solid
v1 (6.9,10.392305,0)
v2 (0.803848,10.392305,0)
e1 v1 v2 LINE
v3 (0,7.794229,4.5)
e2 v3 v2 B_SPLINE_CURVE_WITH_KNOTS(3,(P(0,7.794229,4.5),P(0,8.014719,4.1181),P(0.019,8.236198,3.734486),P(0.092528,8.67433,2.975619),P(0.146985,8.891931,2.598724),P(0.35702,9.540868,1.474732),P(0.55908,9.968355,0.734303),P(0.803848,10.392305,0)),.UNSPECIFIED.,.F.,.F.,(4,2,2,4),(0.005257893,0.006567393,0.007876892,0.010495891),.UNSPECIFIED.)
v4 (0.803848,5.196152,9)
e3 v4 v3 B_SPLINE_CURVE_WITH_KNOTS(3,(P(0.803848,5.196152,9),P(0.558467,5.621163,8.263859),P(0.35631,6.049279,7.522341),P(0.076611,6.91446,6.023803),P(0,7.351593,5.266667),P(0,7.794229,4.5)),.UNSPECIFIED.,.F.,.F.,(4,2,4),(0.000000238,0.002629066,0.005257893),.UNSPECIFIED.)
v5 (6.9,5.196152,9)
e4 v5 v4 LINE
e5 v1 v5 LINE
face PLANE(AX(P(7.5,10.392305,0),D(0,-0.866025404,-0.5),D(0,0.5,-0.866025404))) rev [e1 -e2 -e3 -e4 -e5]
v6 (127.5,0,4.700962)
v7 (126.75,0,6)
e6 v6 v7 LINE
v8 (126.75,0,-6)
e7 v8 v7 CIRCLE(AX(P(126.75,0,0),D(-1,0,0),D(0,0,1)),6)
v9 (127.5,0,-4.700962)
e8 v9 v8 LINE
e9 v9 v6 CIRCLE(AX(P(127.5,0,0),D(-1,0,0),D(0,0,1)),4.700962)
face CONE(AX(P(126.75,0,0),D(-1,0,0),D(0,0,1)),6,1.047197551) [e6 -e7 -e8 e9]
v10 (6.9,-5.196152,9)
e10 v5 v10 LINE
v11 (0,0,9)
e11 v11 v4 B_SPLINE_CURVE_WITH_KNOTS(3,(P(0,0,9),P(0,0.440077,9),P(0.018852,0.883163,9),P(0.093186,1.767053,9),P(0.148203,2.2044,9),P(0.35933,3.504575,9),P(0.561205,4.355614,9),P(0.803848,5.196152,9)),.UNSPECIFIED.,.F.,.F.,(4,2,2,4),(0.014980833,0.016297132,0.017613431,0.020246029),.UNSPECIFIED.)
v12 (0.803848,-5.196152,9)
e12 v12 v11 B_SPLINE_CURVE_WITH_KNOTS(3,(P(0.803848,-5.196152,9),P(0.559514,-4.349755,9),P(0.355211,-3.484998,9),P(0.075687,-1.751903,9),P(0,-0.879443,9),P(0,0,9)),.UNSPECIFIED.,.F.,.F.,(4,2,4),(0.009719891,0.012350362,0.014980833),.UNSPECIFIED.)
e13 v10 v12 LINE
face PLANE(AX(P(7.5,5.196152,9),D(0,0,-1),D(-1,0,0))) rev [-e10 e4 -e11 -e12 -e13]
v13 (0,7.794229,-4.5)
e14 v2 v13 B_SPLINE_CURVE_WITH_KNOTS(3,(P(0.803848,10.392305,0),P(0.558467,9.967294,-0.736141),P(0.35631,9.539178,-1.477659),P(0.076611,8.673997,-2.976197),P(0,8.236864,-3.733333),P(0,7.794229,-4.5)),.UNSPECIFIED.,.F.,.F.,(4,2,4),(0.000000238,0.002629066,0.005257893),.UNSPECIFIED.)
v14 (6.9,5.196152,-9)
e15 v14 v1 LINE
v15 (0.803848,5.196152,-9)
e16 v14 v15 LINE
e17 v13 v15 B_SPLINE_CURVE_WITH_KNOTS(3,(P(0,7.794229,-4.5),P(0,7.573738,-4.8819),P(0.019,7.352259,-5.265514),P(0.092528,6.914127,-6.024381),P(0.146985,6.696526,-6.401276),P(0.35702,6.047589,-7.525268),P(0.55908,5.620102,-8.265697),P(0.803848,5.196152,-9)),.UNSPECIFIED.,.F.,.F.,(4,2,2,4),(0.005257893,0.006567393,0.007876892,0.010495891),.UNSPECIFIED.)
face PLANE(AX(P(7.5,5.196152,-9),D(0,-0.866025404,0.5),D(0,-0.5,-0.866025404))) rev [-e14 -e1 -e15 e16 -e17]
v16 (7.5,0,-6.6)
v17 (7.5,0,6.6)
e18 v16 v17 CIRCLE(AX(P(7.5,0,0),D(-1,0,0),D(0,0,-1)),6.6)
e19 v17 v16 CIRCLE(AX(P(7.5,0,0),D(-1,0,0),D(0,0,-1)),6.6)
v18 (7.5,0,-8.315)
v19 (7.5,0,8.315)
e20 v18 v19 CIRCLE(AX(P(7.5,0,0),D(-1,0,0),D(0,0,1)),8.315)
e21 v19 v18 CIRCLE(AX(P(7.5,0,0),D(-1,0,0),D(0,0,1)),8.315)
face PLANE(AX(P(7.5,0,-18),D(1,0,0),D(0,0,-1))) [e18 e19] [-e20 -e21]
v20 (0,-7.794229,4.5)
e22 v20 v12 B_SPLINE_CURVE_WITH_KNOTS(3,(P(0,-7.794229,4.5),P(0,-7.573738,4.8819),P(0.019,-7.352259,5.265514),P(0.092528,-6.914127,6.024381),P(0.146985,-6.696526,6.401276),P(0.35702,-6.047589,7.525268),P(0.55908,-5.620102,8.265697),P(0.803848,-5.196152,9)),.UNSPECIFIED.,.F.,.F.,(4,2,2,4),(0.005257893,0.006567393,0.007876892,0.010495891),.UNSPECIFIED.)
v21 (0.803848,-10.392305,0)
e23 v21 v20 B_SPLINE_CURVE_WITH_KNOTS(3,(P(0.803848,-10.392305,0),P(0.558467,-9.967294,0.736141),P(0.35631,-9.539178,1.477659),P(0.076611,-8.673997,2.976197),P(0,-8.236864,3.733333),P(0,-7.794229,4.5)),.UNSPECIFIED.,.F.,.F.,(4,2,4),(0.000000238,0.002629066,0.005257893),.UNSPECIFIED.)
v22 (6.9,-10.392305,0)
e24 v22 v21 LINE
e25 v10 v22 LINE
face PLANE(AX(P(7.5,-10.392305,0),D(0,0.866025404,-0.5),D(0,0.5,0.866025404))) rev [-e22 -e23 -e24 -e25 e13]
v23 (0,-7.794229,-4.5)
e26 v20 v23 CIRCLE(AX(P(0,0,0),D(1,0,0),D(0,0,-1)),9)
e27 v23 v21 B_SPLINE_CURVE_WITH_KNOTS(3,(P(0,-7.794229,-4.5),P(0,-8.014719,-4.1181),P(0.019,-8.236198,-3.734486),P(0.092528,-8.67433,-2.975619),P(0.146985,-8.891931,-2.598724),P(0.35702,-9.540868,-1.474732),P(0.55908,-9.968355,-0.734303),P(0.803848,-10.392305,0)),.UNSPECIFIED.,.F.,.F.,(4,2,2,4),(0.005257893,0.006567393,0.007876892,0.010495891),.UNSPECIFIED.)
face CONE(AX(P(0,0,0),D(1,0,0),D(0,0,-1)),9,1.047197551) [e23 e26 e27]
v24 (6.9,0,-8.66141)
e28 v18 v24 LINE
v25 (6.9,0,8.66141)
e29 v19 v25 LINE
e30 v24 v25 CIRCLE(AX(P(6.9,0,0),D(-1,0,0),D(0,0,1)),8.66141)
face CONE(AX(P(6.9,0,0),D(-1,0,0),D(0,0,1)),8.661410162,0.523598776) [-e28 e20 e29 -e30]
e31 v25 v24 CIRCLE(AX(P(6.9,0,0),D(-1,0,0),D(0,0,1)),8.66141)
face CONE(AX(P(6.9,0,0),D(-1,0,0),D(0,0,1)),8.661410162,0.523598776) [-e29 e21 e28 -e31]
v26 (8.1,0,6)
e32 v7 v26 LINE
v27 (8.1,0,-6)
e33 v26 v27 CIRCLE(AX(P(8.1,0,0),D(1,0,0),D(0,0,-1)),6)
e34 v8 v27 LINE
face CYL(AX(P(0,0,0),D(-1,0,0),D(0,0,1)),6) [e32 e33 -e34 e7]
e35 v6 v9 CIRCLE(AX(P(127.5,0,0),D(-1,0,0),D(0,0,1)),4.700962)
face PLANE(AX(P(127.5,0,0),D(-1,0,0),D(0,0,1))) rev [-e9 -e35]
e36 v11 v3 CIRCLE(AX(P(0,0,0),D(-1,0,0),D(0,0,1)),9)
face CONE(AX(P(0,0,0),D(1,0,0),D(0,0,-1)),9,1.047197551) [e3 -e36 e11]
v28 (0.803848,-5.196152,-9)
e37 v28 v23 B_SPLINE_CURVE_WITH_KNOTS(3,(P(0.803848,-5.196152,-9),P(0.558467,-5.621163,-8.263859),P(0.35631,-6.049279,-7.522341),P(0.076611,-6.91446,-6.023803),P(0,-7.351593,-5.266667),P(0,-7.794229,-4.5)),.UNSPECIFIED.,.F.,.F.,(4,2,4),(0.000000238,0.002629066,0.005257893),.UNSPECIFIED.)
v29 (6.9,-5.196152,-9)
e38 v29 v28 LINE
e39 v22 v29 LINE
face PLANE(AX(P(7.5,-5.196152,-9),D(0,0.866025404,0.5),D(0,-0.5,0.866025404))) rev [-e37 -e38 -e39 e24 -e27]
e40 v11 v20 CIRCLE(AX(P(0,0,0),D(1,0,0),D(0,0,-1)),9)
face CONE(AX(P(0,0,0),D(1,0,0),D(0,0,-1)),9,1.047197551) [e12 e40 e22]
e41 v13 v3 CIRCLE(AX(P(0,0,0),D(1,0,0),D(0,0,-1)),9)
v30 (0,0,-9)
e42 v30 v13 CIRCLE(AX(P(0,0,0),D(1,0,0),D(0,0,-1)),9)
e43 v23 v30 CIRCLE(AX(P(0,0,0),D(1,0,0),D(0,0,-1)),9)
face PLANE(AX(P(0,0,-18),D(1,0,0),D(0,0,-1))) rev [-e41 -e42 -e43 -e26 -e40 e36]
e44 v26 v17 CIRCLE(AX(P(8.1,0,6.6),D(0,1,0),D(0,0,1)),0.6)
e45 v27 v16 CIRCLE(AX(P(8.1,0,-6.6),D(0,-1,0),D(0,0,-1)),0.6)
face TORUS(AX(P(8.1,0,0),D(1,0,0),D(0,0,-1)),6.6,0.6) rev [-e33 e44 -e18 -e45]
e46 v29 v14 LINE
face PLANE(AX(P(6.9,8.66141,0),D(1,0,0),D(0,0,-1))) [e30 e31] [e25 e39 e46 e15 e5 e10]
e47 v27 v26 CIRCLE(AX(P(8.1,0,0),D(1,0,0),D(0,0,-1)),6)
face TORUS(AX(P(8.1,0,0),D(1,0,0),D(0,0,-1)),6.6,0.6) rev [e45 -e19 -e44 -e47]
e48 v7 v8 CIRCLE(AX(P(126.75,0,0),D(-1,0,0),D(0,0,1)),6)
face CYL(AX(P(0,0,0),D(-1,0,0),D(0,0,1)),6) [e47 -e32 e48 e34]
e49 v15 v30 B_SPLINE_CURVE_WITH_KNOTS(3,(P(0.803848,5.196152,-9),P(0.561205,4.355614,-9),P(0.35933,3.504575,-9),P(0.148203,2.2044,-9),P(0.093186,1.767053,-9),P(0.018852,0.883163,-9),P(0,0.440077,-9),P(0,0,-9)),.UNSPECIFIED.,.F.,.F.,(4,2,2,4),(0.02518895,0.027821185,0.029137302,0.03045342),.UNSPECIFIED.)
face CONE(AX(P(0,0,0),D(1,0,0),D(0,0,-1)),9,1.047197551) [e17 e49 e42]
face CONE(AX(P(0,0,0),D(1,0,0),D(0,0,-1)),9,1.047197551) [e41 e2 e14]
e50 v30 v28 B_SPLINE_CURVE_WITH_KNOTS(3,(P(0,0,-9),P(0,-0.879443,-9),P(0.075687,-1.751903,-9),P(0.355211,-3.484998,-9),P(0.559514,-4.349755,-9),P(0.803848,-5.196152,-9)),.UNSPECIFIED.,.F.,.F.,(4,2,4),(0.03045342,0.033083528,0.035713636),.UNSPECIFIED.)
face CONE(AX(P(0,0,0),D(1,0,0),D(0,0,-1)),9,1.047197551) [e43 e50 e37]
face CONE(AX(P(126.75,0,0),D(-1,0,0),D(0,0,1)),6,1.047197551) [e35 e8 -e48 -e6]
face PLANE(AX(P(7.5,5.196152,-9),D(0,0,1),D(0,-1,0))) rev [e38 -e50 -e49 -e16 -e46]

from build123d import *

# Parameters (mm, degrees)
EXTRUDE_421_DEPTH = 7.5
FILLET_1347_R     = 0.6


with BuildPart() as part:
    # 草图1 → Extrude 421 (new body)
    with BuildSketch(Plane(origin=(0, 0, 0), x_dir=(0, 0, -1), z_dir=(1, 0, 0))):
        Polygon((9, 5.196152423), (9, -5.196152423), (0, -10.392304845), (-9, -5.196152423), (-9, 5.196152423), (0, 10.392304845), align=None)
    extrude(amount=EXTRUDE_421_DEPTH)

    # 草图2 → 凸台-旋转1 (revolve)
    with BuildSketch(Plane.XY, mode=Mode.PRIVATE) as revolve_1_sk:
        Polygon((0, 0), (127.5, 0), (127.5, 4.701), (127.5, 6), (63.75, 6), (0, 6), align=None)
    revolve(revolve_1_sk.sketch.rotate(Axis((0, 0, 0), (1, 0, 0)), 90), axis=Axis((0, 0, 0), (1, 0, 0)))

    # 草图3 → 切除-旋转1 (revolve, cut)
    with BuildSketch(Plane.XY):
        Polygon((0, 9), (3.690598923, 15.392304845), (3.690598923, 20.392304845), (-10, 20.392304845), (-10, 9), align=None)
    revolve(axis=Axis((0, 0, 0), (1, 0, 0)), mode=Mode.SUBTRACT)

    # 草图4 → 切除-旋转3 (revolve, cut)
    with BuildSketch(Plane.XY, mode=Mode.PRIVATE) as cut_revolve_3_sk:
        Polygon((7.5, 8.315), (6.9, 8.661410162), (6.9, 10.392304845), (7.5, 10.392304845), align=None)
    revolve(cut_revolve_3_sk.sketch.rotate(Axis((0, 0, 0), (1, 0, 0)), 90), axis=Axis((0, 0, 0), (1, 0, 0)), mode=Mode.SUBTRACT)

    # Fillet 1347
    fillet_1347_edges = [part.edges().sort_by_distance(p)[0] for p in [
        (7.5, 0, -6),
    ]]
    fillet(fillet_1347_edges, radius=FILLET_1347_R)

    # 草图6 → 切除-旋转4 (revolve, cut)
    with BuildSketch(Plane.XY, mode=Mode.PRIVATE) as cut_revolve_4_sk:
        Polygon((126.75, 6), (128.25, 6), (127.5, 4.700961894), align=None)
    revolve(cut_revolve_4_sk.sketch.rotate(Axis((0, 0, 0), (1, 0, 0)), 90), axis=Axis((0, 0, 0), (1, 0, 0)), mode=Mode.SUBTRACT)


solid = part.part
